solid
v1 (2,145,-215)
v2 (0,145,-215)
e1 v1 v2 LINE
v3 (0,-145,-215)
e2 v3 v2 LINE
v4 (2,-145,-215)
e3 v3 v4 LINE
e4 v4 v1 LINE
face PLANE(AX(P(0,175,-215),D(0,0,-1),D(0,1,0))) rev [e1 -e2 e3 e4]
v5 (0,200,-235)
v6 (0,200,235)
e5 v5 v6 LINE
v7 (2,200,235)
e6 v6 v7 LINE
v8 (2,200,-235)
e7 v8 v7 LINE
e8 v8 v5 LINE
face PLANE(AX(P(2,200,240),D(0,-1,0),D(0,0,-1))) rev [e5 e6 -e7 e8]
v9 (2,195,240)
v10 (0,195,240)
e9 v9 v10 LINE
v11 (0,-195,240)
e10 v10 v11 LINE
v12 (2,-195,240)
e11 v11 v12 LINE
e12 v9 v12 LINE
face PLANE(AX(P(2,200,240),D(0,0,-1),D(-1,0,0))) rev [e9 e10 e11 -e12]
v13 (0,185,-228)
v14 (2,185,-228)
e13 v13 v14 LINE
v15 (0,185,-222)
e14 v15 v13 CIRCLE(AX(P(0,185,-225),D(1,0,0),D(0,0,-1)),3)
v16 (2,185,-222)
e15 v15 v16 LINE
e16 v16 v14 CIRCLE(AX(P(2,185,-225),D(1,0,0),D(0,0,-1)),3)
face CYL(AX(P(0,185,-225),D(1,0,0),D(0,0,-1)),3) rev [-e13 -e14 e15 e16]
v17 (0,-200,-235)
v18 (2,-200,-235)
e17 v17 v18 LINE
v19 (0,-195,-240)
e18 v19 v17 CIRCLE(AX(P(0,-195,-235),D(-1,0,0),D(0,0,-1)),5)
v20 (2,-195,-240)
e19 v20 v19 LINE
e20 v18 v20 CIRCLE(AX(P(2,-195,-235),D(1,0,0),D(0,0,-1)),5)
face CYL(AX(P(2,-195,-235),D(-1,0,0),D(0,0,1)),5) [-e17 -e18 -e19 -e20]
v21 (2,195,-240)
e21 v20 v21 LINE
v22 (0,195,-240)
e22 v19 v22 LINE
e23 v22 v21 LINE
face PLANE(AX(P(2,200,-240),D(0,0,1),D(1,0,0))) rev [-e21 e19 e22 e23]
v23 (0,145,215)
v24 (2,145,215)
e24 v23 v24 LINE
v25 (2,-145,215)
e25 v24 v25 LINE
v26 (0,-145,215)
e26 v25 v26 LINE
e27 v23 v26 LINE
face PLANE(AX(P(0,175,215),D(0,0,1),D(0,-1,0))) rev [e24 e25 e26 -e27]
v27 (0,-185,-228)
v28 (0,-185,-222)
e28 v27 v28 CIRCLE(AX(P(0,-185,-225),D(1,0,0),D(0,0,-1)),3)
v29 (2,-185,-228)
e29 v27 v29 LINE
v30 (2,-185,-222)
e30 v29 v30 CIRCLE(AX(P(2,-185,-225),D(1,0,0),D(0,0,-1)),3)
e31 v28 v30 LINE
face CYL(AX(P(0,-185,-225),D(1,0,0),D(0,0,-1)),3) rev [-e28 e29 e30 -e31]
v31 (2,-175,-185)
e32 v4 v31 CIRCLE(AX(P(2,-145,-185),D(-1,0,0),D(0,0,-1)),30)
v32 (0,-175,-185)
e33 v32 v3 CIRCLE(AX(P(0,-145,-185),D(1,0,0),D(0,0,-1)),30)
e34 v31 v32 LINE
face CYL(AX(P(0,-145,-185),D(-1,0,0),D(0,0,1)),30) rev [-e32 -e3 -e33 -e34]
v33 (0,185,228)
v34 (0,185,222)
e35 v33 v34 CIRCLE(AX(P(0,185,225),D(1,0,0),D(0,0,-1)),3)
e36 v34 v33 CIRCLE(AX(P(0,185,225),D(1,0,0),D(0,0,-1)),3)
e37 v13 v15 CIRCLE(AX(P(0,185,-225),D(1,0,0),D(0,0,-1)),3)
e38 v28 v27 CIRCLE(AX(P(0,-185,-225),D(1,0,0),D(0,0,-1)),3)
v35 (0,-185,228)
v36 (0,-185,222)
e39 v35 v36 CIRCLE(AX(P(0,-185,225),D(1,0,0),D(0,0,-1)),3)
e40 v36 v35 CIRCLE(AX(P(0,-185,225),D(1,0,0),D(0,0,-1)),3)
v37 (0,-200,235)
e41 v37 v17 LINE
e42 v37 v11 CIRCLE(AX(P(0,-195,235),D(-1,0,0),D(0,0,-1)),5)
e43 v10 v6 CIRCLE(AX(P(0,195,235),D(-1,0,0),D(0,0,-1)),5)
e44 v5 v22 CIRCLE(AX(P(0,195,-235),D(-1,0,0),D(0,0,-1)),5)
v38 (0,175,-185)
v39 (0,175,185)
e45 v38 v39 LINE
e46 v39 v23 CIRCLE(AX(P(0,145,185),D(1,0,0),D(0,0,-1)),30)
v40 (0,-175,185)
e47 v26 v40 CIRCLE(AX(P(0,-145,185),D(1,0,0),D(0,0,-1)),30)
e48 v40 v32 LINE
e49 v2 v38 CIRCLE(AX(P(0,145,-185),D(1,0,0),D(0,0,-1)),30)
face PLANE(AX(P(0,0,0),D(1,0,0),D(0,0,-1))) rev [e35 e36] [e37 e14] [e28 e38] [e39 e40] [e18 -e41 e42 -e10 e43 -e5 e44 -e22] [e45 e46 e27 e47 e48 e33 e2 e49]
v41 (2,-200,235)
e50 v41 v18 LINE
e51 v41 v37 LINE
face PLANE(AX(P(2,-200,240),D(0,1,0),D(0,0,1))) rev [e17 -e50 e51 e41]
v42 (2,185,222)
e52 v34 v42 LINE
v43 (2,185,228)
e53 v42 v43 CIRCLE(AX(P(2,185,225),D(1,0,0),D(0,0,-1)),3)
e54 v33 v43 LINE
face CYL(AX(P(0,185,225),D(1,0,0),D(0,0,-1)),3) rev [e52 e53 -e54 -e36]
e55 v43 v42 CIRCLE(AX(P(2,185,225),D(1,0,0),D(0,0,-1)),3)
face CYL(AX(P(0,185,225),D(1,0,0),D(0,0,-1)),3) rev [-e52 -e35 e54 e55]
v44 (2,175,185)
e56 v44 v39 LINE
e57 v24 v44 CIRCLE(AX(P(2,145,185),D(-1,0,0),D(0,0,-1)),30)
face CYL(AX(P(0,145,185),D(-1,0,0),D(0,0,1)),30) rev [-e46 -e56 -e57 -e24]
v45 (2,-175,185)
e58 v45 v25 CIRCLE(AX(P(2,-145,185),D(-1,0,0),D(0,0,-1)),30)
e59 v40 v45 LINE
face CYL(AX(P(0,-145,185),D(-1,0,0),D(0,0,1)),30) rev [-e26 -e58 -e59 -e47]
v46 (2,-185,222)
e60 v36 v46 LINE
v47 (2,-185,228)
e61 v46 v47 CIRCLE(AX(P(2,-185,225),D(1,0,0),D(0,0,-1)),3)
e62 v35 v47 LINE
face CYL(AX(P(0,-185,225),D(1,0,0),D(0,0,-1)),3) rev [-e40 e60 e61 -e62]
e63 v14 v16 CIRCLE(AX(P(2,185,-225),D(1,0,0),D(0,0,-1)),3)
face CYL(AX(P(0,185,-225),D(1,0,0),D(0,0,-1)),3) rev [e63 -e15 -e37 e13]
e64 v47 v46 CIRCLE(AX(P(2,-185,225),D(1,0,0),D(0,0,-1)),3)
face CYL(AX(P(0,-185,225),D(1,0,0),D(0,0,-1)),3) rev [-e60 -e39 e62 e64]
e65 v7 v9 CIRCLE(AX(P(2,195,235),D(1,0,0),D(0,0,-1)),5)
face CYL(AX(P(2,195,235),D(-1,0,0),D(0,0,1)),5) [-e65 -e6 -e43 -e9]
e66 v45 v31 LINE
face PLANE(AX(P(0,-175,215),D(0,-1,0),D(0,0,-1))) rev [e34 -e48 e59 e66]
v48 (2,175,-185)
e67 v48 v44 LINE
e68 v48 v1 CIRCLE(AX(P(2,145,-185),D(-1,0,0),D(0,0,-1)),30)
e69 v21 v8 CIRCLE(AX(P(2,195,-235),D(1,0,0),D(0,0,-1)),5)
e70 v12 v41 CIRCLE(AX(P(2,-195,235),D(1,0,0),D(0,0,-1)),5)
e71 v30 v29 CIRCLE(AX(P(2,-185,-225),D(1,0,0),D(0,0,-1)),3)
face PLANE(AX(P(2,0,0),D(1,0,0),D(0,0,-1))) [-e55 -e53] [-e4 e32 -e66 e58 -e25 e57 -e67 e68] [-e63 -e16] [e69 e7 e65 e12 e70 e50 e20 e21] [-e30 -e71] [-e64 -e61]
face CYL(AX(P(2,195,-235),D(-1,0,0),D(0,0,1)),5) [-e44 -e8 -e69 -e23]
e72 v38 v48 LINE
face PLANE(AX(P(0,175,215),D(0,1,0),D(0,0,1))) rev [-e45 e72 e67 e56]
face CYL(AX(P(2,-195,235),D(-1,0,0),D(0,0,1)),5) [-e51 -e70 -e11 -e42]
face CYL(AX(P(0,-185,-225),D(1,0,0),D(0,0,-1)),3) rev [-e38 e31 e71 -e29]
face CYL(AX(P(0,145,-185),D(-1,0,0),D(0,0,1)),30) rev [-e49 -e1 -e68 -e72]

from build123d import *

# Parameters (mm, degrees)
SKETCH_1_W          = 480
SKETCH_1_H          = 400
EXTRUDE_1_DEPTH     = 2
SKETCH_2_R          = 3
CUT_EXTRUDE_1_DEPTH = 313.416388815
FILLET_1_R          = 5
SKETCH_3_W          = 430
SKETCH_3_H          = 350
CUT_EXTRUDE_2_DEPTH = 313.416388815
FILLET_2_R          = 30


with BuildPart() as part:
    # 草图1 → 凸台-拉伸1 (new body)
    with BuildSketch(Plane(origin=(0, 0, 0), x_dir=(0, 0, -1), z_dir=(1, 0, 0))):
        Rectangle(SKETCH_1_W, SKETCH_1_H)
    extrude(amount=EXTRUDE_1_DEPTH)

    # 草图2 → 切除-拉伸1 (cut, through all)
    with BuildSketch(Plane(origin=(2, 0, 0), x_dir=(0, 0, -1), z_dir=(1, 0, 0))):
        with Locations((-225, 185)):
            Circle(SKETCH_2_R)
        with Locations((225, 185)):
            Circle(SKETCH_2_R)
        with Locations((-225, -185)):
            Circle(SKETCH_2_R)
        with Locations((225, -185)):
            Circle(SKETCH_2_R)
    extrude(amount=-CUT_EXTRUDE_1_DEPTH, mode=Mode.SUBTRACT)

    # 圆角1
    fillet_1_edges = [part.edges().sort_by_distance(p)[0] for p in [
        (1, 200, 240),
        (1, 200, -240),
        (1, -200, -240),
        (1, -200, 240),
    ]]
    fillet(fillet_1_edges, radius=FILLET_1_R)

    # 草图3 → 切除-拉伸2 (cut, through all)
    with BuildSketch(Plane(origin=(2, 0, 0), x_dir=(0, 0, -1), z_dir=(1, 0, 0))):
        Rectangle(SKETCH_3_W, SKETCH_3_H)
    extrude(amount=-CUT_EXTRUDE_2_DEPTH, mode=Mode.SUBTRACT)

    # 圆角2
    fillet_2_edges = [part.edges().sort_by_distance(p)[0] for p in [
        (1, -175, 215),
        (1, 175, 215),
        (1, 175, -215),
        (1, -175, -215),
    ]]
    fillet(fillet_2_edges, radius=FILLET_2_R)


solid = part.part
